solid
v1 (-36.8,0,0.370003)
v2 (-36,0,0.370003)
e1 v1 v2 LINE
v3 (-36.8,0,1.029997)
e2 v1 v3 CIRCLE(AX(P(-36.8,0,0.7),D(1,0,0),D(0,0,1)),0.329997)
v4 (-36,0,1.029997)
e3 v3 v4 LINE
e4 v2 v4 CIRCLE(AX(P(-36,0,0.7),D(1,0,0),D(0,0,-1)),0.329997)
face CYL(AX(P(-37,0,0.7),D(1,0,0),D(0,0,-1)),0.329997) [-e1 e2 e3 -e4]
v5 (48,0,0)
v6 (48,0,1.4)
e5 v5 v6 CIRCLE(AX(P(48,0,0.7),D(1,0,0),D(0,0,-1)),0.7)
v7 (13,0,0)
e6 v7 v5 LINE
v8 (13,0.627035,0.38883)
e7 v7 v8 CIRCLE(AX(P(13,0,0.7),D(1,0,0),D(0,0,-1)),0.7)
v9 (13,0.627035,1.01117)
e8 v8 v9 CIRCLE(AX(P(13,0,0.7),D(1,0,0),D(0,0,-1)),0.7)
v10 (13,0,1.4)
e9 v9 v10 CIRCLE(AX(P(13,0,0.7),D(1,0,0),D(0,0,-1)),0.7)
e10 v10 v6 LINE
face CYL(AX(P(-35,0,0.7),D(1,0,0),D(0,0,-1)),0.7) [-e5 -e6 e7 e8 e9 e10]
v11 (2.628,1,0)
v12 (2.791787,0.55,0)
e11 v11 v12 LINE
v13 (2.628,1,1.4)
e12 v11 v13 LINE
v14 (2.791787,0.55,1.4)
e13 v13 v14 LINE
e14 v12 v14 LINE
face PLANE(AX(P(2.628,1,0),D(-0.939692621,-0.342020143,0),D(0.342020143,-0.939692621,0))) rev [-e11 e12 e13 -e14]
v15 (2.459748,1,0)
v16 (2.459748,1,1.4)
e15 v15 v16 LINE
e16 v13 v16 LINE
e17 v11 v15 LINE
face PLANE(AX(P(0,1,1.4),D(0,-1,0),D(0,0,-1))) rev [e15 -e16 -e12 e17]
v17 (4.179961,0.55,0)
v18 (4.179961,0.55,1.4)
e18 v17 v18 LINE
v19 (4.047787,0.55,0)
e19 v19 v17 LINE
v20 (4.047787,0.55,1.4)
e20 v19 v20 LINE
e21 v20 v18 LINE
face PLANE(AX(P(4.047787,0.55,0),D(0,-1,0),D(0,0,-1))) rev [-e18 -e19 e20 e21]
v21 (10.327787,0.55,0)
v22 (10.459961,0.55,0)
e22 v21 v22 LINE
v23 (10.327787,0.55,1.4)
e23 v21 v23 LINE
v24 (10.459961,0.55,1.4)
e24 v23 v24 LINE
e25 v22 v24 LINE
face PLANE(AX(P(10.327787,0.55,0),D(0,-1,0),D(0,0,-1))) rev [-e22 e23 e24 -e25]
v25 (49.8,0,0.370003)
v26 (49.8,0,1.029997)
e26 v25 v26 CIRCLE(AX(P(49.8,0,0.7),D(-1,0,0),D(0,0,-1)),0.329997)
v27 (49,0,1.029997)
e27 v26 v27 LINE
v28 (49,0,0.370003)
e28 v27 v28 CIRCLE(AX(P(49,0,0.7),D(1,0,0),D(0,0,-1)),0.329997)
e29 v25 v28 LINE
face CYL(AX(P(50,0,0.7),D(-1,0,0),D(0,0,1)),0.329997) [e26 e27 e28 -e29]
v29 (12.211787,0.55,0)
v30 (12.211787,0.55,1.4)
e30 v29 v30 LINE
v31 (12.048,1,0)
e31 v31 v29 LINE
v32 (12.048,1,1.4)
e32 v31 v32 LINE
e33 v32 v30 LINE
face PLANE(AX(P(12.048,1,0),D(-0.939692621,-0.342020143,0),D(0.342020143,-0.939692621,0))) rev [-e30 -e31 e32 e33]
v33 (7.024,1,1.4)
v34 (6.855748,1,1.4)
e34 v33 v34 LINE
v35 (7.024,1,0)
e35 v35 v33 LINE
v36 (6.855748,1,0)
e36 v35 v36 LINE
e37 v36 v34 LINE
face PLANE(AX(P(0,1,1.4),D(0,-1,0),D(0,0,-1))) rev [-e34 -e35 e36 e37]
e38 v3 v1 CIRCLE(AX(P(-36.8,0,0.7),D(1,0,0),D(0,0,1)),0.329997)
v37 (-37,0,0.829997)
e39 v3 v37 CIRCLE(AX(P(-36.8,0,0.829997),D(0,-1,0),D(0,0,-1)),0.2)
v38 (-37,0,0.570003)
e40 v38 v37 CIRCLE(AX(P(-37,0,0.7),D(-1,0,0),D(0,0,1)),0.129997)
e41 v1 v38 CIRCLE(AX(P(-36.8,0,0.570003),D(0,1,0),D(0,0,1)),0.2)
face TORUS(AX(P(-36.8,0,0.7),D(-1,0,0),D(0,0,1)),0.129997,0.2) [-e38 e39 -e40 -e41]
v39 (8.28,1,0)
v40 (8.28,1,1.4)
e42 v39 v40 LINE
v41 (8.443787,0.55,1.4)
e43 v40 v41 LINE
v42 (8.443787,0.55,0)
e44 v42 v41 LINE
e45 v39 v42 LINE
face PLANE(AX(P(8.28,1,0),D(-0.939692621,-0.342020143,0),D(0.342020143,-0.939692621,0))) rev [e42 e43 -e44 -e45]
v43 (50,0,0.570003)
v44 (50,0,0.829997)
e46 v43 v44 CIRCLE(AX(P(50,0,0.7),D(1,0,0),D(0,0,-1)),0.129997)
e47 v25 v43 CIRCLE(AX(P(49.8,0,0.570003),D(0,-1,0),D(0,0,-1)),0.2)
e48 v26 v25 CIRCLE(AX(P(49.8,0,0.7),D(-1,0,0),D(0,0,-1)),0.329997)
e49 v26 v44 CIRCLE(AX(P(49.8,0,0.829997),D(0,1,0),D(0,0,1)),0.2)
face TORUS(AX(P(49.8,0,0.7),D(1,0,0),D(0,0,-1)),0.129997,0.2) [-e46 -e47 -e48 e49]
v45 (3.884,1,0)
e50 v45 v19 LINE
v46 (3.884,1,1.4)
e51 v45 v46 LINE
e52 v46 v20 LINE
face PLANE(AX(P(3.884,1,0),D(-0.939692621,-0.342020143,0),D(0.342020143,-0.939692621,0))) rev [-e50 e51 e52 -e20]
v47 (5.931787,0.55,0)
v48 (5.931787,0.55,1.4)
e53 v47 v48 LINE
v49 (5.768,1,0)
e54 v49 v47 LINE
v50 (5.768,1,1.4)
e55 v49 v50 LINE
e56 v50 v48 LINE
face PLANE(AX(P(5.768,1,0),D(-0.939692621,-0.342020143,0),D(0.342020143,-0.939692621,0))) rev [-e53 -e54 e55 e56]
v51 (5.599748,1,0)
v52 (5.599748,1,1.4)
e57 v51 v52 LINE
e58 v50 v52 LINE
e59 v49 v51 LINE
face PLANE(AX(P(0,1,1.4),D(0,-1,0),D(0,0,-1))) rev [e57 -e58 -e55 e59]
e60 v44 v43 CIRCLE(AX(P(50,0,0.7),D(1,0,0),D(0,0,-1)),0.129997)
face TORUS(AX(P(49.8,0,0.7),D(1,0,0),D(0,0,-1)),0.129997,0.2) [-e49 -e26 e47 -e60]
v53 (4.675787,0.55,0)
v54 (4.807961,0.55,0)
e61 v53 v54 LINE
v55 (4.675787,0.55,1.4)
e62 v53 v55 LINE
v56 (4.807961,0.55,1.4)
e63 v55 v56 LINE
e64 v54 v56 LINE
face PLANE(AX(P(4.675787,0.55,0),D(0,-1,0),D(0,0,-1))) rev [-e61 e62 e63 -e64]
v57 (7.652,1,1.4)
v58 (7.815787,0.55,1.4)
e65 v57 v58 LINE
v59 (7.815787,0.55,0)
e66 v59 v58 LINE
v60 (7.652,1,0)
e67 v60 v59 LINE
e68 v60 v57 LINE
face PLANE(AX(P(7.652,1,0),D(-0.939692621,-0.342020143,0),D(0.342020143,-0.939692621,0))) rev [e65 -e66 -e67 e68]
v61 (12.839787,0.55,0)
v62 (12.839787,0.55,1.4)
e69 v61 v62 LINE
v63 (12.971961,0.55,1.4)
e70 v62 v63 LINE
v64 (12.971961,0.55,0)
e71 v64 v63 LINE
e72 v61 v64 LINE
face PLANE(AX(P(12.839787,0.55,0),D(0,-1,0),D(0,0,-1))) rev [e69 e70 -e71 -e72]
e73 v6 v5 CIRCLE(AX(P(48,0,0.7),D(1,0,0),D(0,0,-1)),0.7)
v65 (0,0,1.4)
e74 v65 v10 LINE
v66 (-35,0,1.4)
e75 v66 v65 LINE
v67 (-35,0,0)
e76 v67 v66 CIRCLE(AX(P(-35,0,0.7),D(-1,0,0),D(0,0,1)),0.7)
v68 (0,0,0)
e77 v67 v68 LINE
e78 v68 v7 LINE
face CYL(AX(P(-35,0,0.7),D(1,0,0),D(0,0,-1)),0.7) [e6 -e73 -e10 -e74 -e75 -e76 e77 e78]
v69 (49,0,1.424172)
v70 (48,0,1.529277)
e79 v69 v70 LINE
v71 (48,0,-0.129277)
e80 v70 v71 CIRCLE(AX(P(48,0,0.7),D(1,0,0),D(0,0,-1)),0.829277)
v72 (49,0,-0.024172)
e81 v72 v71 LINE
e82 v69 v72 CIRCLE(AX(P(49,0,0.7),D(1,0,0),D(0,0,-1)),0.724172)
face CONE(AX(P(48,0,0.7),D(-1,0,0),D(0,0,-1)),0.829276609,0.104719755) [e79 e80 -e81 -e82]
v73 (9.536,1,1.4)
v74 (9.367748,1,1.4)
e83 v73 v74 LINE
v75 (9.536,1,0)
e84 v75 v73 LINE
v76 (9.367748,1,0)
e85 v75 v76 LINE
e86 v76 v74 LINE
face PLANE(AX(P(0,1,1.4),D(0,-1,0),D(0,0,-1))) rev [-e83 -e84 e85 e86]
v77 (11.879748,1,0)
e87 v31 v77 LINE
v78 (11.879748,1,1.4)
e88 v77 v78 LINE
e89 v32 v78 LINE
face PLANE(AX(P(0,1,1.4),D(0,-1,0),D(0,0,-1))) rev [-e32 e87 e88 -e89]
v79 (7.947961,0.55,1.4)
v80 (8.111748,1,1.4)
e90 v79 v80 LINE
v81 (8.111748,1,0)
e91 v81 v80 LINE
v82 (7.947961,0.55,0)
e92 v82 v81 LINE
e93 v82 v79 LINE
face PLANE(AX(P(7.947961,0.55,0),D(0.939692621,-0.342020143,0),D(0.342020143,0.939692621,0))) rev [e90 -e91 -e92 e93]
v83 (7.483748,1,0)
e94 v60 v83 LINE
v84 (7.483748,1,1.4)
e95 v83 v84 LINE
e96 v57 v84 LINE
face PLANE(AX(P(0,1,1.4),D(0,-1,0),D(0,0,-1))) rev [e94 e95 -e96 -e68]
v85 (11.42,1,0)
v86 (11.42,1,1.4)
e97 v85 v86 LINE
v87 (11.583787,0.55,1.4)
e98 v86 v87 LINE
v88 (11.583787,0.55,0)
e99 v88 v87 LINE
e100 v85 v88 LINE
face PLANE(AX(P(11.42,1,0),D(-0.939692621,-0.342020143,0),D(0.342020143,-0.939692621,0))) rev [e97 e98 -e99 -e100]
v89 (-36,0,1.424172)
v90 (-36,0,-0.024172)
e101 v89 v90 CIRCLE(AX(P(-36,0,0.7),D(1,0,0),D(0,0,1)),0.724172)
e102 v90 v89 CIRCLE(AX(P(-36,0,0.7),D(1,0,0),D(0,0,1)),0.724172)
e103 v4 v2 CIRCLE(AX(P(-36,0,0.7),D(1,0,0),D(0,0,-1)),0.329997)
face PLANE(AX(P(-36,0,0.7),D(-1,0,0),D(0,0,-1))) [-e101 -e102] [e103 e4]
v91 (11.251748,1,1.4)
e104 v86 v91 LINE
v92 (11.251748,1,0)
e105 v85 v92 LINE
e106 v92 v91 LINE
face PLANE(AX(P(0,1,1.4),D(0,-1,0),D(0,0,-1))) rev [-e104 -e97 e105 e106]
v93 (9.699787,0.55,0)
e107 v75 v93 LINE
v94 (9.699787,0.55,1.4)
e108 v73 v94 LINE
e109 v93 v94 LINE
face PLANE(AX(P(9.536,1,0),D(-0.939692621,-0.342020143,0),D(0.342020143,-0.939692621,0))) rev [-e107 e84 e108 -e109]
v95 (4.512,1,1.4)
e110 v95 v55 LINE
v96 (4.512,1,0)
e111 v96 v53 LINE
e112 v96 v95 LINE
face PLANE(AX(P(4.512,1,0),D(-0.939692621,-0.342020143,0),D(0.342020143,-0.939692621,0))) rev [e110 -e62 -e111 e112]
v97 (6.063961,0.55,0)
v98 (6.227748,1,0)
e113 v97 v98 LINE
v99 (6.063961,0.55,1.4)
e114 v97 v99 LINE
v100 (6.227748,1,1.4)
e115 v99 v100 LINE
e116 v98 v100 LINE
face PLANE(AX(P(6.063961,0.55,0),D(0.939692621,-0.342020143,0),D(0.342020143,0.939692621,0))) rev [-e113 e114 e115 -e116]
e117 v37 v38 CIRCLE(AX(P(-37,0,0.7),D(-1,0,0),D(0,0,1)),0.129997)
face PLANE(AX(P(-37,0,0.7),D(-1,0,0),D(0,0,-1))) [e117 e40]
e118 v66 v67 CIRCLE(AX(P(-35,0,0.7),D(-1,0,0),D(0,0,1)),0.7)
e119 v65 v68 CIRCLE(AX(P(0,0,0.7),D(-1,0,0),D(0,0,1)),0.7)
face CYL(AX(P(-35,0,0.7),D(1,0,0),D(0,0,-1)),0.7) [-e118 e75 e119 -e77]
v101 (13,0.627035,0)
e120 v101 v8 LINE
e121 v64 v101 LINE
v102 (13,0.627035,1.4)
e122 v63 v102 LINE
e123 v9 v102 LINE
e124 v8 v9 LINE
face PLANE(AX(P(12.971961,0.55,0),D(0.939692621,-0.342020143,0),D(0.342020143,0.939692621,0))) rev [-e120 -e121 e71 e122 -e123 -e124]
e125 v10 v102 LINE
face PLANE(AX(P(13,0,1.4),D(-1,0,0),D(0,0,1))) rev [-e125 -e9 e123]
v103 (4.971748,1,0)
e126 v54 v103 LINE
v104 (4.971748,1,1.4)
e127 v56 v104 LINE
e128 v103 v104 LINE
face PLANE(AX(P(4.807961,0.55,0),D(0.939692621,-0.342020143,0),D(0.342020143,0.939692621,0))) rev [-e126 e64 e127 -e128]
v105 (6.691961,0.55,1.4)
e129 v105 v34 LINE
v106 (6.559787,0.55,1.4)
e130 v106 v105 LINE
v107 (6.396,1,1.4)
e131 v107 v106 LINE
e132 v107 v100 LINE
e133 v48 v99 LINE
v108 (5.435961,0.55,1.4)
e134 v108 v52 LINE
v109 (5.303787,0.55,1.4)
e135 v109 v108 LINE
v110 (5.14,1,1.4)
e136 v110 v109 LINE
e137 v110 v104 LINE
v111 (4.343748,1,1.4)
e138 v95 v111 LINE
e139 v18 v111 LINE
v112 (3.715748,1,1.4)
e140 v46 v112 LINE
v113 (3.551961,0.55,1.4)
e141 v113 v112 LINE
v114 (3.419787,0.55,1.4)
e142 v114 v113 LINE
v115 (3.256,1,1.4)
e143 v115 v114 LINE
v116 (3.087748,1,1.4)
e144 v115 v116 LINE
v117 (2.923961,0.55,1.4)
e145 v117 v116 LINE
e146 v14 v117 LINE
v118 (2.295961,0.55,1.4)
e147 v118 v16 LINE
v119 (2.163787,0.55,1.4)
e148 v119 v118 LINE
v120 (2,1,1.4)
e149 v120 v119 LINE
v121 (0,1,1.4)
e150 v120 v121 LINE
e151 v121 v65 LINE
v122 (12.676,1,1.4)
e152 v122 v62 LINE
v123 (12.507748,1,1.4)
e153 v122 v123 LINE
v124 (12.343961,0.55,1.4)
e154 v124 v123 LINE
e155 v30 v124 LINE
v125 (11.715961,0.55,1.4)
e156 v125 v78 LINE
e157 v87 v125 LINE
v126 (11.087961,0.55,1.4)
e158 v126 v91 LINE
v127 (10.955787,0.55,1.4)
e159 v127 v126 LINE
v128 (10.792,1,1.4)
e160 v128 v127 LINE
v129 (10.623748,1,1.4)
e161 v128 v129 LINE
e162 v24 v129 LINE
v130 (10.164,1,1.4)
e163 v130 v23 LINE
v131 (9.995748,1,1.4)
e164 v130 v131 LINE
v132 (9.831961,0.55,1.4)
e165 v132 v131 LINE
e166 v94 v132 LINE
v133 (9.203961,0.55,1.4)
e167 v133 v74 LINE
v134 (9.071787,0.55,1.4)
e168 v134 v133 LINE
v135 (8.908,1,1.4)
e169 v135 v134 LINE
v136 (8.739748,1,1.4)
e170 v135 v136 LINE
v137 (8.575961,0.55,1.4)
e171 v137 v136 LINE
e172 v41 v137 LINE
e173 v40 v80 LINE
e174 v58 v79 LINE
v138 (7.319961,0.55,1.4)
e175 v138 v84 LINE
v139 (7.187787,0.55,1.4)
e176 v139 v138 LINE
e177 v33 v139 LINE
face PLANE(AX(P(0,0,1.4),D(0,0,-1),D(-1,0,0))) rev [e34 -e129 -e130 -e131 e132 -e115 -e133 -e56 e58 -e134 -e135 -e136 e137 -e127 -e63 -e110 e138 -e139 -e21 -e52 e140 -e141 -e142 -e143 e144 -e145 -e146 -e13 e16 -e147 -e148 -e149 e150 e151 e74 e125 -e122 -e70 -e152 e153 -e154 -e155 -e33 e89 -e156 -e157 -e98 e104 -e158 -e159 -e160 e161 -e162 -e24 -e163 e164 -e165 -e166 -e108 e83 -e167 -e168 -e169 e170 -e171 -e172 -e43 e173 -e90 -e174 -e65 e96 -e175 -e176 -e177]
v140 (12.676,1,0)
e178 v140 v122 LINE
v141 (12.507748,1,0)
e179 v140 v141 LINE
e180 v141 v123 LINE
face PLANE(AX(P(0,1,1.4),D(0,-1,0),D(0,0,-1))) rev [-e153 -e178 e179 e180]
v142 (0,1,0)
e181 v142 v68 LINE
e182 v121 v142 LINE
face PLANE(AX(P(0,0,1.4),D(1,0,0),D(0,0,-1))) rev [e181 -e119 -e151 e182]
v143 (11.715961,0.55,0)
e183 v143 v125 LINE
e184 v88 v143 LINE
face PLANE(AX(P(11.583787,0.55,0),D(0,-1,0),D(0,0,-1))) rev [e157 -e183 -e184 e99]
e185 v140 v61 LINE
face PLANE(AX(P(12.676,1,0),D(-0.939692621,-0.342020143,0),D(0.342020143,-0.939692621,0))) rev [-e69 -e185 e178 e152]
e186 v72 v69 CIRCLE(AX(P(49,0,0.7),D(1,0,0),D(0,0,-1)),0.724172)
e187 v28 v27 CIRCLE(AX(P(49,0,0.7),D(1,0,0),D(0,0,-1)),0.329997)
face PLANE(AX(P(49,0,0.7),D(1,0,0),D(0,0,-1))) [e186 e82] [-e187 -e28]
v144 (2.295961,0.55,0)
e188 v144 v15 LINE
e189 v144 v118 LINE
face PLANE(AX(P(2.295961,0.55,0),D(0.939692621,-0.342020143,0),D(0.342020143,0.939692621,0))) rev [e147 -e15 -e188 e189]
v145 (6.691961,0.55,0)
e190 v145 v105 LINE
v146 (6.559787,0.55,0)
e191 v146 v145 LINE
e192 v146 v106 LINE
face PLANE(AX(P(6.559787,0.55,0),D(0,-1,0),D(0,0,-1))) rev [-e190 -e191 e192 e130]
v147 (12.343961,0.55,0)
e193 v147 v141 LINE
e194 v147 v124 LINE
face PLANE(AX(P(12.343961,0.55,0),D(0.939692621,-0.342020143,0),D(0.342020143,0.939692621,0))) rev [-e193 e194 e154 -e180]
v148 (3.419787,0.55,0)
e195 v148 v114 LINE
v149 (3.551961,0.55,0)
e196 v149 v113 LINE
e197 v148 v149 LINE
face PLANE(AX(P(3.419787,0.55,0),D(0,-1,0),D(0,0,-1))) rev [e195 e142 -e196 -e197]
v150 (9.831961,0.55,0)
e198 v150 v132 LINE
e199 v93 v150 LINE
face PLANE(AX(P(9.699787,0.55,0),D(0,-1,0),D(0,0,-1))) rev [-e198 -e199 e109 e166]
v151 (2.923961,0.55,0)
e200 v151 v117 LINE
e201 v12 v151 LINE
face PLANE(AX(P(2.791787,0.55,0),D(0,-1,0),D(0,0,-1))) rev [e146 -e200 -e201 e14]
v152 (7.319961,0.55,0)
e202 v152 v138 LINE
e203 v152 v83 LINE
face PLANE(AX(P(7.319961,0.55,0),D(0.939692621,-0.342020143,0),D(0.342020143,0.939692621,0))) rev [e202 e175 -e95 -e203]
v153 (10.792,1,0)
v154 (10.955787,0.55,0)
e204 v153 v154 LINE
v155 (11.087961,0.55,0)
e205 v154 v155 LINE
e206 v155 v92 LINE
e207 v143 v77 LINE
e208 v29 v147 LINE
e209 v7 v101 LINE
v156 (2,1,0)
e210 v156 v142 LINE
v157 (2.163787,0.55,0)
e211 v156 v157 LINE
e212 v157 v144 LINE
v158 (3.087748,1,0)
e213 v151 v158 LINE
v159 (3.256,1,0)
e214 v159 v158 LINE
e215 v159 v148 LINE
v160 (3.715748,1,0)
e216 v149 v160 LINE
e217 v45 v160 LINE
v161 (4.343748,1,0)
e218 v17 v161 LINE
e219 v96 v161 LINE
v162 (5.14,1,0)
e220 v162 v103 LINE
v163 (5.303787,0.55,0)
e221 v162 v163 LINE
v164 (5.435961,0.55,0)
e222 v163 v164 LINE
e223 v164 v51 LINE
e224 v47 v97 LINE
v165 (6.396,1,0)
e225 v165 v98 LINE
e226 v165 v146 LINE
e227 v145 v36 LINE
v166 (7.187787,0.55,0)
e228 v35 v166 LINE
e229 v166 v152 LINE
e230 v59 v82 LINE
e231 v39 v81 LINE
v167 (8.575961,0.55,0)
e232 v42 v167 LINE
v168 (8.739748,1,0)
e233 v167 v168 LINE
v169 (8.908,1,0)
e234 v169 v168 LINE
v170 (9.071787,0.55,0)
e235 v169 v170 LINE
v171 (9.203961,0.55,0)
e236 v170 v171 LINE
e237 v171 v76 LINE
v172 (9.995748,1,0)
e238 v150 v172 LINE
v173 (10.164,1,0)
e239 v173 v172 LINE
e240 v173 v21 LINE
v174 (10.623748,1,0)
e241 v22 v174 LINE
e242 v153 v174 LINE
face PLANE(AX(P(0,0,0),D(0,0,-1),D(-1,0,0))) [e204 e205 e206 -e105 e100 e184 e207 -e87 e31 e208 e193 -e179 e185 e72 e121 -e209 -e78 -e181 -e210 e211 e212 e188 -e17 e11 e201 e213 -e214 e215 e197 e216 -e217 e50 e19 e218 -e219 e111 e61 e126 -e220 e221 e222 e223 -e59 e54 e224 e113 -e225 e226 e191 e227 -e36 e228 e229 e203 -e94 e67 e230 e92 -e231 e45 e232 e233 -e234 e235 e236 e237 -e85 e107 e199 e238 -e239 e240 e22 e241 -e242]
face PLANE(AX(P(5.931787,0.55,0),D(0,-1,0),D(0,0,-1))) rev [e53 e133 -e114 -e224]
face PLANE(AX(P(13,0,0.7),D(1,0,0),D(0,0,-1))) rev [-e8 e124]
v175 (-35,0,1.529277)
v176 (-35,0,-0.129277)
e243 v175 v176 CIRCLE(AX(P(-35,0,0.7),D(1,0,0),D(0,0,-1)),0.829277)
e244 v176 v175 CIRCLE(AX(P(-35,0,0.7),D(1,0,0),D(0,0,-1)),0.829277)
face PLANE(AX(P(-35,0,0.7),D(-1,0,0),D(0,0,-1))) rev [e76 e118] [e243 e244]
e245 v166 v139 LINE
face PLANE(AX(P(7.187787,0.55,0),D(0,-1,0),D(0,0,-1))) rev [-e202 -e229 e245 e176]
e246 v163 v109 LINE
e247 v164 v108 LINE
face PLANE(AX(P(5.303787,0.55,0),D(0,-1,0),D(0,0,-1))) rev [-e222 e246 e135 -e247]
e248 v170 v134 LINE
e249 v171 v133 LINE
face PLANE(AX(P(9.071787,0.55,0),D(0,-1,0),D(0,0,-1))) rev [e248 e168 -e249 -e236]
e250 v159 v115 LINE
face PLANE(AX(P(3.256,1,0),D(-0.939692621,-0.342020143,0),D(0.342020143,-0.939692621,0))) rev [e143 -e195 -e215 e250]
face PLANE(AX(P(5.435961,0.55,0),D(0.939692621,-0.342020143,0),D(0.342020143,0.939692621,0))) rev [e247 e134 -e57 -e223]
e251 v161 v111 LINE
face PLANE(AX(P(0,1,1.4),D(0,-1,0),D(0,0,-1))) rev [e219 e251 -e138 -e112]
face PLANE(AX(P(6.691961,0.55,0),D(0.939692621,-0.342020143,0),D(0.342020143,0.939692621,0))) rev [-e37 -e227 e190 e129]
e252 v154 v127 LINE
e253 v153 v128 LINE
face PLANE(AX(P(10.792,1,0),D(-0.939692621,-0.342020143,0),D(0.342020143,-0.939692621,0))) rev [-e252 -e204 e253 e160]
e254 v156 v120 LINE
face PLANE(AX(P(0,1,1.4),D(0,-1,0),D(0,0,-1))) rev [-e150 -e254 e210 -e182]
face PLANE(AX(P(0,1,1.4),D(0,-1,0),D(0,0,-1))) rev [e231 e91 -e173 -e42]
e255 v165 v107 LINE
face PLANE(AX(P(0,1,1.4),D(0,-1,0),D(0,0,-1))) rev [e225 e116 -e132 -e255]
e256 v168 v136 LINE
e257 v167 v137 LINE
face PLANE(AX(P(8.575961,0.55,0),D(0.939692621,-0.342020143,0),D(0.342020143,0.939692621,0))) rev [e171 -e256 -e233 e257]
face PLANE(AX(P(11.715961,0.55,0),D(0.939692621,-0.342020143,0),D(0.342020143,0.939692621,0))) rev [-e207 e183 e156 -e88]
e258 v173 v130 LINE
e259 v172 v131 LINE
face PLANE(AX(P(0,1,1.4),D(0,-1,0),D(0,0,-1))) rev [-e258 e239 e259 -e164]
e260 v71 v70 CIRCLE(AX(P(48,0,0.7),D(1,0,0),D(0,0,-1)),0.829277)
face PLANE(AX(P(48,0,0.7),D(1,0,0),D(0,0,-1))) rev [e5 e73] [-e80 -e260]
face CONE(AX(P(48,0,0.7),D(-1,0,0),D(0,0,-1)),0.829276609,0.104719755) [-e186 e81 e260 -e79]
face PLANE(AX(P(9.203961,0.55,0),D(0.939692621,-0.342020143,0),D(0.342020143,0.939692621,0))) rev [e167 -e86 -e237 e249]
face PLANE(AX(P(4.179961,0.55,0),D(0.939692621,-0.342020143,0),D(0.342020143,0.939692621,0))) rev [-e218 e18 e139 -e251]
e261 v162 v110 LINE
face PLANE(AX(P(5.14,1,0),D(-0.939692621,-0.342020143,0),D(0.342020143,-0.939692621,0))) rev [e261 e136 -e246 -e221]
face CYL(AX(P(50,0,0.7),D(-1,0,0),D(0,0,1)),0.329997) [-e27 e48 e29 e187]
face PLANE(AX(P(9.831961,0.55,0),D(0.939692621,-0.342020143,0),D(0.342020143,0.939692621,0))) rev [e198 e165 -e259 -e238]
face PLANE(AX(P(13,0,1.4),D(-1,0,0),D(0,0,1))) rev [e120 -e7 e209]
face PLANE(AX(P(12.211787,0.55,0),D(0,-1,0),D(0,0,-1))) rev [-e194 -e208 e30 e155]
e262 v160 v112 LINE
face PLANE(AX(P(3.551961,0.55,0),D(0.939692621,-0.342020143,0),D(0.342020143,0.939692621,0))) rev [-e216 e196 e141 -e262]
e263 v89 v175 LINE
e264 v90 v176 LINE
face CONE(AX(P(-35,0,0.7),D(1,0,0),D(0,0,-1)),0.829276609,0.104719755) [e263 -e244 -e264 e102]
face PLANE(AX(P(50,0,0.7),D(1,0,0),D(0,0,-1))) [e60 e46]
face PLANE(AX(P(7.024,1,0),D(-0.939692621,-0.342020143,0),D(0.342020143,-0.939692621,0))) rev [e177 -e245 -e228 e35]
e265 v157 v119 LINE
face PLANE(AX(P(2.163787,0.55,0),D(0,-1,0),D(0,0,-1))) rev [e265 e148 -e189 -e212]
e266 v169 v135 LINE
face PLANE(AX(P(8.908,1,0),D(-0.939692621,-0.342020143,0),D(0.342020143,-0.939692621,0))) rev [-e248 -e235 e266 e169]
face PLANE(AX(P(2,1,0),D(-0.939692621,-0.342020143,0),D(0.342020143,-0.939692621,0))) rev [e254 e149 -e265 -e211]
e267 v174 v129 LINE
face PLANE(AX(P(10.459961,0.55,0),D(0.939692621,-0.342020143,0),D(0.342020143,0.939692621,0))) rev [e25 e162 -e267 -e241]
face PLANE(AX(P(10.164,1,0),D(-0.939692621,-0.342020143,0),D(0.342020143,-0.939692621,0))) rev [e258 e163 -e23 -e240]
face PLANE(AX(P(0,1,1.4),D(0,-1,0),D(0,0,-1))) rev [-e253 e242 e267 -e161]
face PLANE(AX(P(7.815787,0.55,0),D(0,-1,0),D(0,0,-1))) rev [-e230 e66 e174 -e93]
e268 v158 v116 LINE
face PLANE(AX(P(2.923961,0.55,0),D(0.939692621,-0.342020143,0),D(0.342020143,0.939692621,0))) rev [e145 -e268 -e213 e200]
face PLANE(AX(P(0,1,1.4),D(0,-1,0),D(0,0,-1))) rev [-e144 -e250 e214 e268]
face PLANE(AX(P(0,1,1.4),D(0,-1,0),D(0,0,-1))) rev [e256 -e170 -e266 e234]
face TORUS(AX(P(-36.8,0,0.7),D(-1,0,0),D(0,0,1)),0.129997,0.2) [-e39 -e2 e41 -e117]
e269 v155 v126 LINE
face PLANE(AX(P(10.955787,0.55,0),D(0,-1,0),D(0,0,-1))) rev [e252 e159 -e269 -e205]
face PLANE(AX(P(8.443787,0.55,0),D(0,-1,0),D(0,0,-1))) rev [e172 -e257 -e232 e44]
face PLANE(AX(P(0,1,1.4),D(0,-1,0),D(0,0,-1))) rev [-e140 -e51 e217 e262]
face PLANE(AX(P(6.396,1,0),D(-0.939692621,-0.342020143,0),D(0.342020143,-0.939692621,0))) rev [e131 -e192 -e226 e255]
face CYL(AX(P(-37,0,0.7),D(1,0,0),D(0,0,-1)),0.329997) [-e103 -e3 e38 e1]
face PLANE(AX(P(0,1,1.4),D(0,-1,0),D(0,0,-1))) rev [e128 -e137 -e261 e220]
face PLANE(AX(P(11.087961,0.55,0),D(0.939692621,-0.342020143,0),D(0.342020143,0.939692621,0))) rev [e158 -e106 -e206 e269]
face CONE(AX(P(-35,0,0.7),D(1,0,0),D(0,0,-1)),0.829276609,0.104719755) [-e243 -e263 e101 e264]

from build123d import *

# Parameters (mm, degrees)
SKETCH1_W            = 13
SKETCH1_H            = 1
BOSS_EXTRUDE1_DEPTH  = 1.4
CUT_EXTRUDE1_DEPTH   = 14.113351974
LPATTERN1_COUNT      = 18
LPATTERN1_PITCH      = 0.628
SKETCH3_R            = 0.7
BOSS_EXTRUDE2_DEPTH  = 35
BOSS_EXTRUDE3_START  = 13
BOSS_EXTRUDE3_DEPTH  = 13
BOSS_EXTRUDE4_START  = 35
SKETCH5_R            = 0.7
BOSS_EXTRUDE4_DEPTH  = 35
SKETCH6_R            = 0.829276609
BOSS_EXTRUDE5_DEPTH  = 1
BOSS_EXTRUDE5_TAPER  = 6
SKETCH7_R            = 0.329996585
BOSS_EXTRUDE6_DEPTH  = 1
FILLET1_R            = 0.2
FILLET1_OF_MIRROR1_R = 0.2


with BuildPart() as part:
    # Sketch1 → Boss-Extrude1 (new body)
    with BuildSketch(Plane.XY):
        with Locations((6.5, 0.5)):
            Rectangle(SKETCH1_W, SKETCH1_H)
    extrude(amount=BOSS_EXTRUDE1_DEPTH)

    # Sketch2 → Cut-Extrude1 (cut, through all)
    with BuildSketch(Plane.XY.offset(1.4)):
        Polygon((2, 1), (2.163786605, 0.55), (2.295961488, 0.55), (2.459748094, 1), align=None)
    cut_extrude1 = extrude(amount=-CUT_EXTRUDE1_DEPTH, mode=Mode.SUBTRACT)

    # LPattern1: Cut-Extrude1 ×18
    with Locations(*[(i * LPATTERN1_PITCH, 0, 0) for i in range(1, LPATTERN1_COUNT)]):
        add(cut_extrude1, mode=Mode.SUBTRACT)

    # Sketch3 → Boss-Extrude2 (add)
    with BuildSketch(Plane.ZY):
        with Locations((0.7, 0)):
            Circle(SKETCH3_R)
    extrude(amount=BOSS_EXTRUDE2_DEPTH)

    # Sketch4 → Boss-Extrude3 (add)
    with BuildSketch(Plane(origin=(0, 0, 0), x_dir=(0, 0, -1), z_dir=(1, 0, 0)).offset(BOSS_EXTRUDE3_START)):
        with BuildLine():
            Line((0, 0), (-1.4, 0))
            ThreePointArc((-1.4, 0), (-0.7, -0.7), (0, 0))
        make_face()
    extrude(amount=-BOSS_EXTRUDE3_DEPTH)

    # Sketch5 → Boss-Extrude4 (add)
    with BuildSketch(Plane(origin=(13, 0, 0), x_dir=(0, 0, -1), z_dir=(1, 0, 0)).offset(BOSS_EXTRUDE4_START)):
        with Locations((-0.7, 0)):
            Circle(SKETCH5_R)
    extrude(amount=-BOSS_EXTRUDE4_DEPTH)

    # Sketch6 → Boss-Extrude5 (add)
    with BuildSketch(Plane(origin=(48, 0, 0), x_dir=(0, 0, -1), z_dir=(1, 0, 0))):
        with Locations((-0.7, 0)):
            Circle(SKETCH6_R)
    boss_extrude5 = extrude(amount=BOSS_EXTRUDE5_DEPTH, taper=BOSS_EXTRUDE5_TAPER)

    # Sketch7 → Boss-Extrude6 (add)
    with BuildSketch(Plane(origin=(49, 0, 0), x_dir=(0, 0, -1), z_dir=(1, 0, 0))):
        with Locations((-0.7, 0)):
            Circle(SKETCH7_R)
    boss_extrude6 = extrude(amount=BOSS_EXTRUDE6_DEPTH)

    # Fillet1
    fillet1_edges = [part.edges().sort_by_distance(p)[0] for p in [
        (50, 0, 1.029996585),
    ]]
    fillet(fillet1_edges, radius=FILLET1_R)

    # Mirror1: Boss-Extrude5, Boss-Extrude6 across plane
    add(boss_extrude5.mirror(Plane.ZY.offset(-6.5)))
    add(boss_extrude6.mirror(Plane.ZY.offset(-6.5)))

    # Fillet1 of Mirror1
    fillet1_of_mirror1_edges = [part.edges().sort_by_distance(p)[0] for p in [
        (-37, 0, 1.029996585),
    ]]
    fillet(fillet1_of_mirror1_edges, radius=FILLET1_OF_MIRROR1_R)


solid = part.part
